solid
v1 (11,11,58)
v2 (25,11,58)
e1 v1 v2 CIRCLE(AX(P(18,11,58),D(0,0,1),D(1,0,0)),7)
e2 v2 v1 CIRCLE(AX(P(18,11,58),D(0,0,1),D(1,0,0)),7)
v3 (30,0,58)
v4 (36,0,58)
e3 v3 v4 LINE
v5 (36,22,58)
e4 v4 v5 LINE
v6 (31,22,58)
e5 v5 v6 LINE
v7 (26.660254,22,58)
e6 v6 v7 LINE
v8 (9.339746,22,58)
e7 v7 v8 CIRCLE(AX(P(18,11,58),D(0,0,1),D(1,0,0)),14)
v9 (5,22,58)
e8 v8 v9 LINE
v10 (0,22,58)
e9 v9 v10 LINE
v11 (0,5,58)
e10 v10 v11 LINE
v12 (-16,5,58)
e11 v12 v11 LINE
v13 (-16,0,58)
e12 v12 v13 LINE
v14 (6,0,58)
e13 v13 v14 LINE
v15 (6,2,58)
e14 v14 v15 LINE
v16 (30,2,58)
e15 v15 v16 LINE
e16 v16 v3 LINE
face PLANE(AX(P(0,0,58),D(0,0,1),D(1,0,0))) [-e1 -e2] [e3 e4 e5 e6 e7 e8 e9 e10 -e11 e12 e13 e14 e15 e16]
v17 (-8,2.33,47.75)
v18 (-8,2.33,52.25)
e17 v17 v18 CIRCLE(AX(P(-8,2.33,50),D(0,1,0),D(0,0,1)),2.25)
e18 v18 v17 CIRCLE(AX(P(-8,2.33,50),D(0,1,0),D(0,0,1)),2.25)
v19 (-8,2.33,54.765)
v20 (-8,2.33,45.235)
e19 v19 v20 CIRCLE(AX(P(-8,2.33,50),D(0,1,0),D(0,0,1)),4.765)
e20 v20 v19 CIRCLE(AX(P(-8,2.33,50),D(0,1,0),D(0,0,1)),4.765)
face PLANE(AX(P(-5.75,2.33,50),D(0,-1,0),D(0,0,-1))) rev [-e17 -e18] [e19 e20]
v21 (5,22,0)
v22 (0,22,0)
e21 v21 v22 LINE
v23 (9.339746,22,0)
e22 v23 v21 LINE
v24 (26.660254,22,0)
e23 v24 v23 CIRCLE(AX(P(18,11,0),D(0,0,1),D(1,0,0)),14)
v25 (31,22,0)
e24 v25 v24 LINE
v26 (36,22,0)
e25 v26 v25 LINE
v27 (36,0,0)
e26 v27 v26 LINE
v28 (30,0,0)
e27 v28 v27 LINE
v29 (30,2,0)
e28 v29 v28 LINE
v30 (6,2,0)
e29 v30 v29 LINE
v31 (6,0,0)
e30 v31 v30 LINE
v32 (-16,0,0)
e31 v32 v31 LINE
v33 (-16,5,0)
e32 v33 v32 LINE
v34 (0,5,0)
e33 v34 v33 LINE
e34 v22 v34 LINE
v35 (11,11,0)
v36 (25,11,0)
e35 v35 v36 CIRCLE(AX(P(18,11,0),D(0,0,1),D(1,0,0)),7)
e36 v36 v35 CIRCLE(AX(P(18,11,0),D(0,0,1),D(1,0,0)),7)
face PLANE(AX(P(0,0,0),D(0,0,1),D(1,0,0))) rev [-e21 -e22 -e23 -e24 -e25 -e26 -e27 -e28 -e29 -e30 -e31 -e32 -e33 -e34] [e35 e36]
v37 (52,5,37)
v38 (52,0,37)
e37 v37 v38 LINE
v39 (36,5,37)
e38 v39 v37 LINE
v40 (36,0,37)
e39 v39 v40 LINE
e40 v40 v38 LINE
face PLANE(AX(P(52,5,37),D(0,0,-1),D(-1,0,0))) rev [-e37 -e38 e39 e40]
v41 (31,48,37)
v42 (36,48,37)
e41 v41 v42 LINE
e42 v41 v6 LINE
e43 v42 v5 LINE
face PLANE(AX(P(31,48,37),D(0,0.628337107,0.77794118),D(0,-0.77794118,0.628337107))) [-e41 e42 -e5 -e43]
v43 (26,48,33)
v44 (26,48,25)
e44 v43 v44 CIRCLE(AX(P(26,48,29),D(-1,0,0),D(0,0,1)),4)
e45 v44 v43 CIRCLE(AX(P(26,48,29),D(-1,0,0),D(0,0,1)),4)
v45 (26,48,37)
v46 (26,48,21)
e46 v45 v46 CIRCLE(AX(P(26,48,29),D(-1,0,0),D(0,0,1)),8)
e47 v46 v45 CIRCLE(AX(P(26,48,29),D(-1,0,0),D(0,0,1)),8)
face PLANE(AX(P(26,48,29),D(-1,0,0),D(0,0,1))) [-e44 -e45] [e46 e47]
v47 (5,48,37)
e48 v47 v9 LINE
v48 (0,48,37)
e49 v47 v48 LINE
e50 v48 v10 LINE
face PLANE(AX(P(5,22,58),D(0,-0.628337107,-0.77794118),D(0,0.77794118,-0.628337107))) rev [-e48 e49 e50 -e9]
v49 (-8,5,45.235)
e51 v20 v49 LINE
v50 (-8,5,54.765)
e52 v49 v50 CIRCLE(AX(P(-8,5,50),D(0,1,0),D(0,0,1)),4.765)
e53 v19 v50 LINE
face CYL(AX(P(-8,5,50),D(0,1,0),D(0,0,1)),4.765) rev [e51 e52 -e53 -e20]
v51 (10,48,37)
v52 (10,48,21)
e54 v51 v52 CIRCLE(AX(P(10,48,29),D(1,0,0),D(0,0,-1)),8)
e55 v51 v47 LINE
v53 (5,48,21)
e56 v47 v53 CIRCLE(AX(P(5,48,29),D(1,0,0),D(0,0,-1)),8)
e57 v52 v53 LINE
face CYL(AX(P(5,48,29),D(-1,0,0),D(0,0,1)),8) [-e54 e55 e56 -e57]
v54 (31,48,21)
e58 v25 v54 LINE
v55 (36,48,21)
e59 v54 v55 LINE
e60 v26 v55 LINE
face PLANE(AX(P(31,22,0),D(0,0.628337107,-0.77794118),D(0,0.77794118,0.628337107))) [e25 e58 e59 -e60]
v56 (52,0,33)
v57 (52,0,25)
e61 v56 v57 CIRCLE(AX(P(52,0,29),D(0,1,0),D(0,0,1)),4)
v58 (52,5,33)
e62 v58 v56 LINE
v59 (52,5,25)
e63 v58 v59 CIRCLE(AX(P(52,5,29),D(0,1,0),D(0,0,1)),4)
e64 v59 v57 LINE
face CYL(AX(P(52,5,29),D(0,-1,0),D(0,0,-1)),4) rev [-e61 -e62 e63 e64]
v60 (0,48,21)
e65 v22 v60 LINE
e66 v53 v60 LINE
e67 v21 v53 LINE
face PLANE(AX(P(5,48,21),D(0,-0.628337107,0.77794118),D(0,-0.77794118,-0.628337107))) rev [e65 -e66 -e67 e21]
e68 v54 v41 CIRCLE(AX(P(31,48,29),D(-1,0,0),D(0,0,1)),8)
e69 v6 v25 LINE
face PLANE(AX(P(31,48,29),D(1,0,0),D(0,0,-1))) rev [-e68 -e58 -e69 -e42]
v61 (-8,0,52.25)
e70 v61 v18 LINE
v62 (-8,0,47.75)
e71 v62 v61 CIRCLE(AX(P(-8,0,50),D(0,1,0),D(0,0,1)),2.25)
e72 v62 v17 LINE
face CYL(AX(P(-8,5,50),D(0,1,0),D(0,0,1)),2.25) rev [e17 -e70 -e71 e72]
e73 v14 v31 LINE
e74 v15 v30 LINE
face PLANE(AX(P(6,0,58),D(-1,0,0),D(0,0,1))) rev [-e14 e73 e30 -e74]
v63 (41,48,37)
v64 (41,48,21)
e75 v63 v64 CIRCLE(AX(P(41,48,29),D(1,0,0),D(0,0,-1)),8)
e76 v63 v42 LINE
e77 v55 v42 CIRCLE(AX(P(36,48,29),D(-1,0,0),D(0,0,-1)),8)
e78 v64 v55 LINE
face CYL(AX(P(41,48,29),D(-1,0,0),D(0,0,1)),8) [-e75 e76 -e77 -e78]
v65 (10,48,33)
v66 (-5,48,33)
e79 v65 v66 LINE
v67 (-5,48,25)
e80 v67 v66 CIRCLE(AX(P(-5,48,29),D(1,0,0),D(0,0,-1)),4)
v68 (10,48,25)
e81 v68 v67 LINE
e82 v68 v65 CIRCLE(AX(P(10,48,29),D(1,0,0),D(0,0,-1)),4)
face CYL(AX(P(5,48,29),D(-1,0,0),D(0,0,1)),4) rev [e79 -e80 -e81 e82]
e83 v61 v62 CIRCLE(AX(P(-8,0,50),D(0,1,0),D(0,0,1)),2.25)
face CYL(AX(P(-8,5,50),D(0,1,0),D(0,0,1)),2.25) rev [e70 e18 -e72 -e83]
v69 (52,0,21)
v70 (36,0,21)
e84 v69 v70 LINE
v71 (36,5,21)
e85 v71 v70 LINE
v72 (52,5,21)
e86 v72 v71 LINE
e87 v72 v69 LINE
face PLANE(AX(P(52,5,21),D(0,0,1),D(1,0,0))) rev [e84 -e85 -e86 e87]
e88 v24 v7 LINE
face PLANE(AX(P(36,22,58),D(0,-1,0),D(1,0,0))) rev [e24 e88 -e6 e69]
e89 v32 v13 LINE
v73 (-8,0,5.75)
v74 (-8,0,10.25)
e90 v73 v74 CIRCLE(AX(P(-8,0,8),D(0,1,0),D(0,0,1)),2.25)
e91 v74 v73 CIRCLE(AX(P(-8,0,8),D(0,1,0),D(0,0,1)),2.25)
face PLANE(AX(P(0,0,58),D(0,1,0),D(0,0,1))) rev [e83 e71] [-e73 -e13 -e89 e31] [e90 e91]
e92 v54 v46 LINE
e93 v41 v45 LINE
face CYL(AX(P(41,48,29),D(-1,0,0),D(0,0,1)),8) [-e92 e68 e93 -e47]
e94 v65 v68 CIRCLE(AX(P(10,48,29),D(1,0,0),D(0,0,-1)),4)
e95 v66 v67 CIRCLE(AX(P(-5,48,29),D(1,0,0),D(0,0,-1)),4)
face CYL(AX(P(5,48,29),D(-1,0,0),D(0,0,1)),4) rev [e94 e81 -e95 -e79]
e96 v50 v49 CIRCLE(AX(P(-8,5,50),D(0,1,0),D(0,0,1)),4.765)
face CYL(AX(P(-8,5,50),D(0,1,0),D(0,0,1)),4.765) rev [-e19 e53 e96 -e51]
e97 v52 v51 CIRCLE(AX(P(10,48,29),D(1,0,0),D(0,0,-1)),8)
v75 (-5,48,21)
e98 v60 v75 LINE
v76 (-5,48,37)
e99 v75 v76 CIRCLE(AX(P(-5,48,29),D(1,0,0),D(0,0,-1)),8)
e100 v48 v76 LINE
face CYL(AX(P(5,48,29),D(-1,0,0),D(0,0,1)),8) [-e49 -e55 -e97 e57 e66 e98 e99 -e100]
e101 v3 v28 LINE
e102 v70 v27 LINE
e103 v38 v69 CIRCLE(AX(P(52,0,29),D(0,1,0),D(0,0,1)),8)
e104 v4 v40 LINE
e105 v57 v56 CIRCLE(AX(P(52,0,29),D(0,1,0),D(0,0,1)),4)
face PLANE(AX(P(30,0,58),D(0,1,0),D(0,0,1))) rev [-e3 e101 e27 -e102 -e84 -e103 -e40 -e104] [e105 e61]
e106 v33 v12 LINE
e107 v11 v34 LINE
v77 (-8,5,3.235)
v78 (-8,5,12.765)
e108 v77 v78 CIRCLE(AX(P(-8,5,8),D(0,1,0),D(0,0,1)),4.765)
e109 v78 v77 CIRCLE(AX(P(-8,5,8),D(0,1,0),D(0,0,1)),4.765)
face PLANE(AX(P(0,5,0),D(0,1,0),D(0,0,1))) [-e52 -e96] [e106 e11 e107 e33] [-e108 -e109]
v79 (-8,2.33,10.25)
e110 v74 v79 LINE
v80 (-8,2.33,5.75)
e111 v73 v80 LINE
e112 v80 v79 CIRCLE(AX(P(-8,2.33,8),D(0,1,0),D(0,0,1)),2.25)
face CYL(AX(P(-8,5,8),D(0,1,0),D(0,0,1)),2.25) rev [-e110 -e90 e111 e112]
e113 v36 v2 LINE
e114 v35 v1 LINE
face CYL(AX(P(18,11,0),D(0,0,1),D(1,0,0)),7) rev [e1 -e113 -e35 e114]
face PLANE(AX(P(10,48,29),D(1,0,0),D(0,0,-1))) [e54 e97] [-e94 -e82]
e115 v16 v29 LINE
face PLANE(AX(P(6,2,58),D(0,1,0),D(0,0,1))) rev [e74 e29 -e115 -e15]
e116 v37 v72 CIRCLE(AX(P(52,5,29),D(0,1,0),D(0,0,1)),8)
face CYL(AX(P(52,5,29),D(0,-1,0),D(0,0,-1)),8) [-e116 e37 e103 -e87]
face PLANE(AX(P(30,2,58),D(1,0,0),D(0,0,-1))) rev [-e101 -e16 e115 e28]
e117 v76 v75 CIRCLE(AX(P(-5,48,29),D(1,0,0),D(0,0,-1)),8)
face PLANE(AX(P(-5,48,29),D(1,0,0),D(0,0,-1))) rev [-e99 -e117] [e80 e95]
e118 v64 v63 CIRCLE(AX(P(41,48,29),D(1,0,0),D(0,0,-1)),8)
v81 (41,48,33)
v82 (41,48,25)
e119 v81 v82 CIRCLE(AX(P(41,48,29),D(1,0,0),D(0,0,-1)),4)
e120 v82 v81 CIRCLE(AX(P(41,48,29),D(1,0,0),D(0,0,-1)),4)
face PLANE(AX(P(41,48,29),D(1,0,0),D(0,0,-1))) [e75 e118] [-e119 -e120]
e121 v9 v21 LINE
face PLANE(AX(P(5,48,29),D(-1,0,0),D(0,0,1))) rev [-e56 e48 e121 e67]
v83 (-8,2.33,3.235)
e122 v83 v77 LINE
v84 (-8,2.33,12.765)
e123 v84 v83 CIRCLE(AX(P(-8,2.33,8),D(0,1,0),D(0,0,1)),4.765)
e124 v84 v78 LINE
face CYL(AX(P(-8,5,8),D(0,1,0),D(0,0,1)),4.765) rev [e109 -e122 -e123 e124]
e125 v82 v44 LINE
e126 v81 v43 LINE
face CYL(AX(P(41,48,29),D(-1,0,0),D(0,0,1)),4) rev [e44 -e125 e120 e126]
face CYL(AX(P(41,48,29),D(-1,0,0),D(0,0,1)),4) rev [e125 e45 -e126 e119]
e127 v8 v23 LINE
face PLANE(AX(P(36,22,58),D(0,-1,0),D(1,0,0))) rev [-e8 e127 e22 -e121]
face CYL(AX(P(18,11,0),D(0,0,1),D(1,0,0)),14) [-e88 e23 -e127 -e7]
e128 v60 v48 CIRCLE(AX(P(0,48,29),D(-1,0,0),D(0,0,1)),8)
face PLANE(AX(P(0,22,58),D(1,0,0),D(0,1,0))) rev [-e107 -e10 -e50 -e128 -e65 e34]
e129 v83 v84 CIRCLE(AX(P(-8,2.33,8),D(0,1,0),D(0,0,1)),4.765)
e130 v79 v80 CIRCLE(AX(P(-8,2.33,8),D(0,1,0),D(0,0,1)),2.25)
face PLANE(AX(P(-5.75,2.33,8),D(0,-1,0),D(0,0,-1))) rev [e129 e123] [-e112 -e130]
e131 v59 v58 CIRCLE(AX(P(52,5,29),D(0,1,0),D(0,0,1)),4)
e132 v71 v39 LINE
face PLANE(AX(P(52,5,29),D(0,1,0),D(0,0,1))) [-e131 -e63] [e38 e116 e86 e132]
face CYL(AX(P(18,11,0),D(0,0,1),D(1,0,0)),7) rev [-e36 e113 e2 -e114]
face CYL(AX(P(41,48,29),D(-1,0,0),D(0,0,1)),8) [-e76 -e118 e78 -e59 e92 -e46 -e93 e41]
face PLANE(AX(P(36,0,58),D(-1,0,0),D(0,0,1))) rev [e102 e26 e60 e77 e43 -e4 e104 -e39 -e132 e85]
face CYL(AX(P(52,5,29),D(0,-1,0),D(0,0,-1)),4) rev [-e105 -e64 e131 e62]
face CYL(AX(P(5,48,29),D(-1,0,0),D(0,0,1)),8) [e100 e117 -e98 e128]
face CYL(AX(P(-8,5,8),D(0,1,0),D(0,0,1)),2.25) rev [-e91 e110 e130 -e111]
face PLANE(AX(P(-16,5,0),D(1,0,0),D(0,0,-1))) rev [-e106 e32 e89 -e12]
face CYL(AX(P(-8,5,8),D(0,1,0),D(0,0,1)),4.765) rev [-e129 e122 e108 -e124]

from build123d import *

# Parameters (mm, degrees)
BASE_BLOCK_DEPTH                = 58
FRONT_BORE_BOSS_DEPTH           = 58
FRONT_BORE_SKETCH_R             = 7
FRONT_BORE_DEPTH                = 73.698005475
LEFT_ARM_SKETCH_R               = 8
LEFT_ARM_SKETCH_R_2             = 4
LEFT_ARM_DEPTH                  = 5
LEFT_ARM_WEB_DEPTH              = 5
LEFT_START                      = 5
LEFT_PIVOT_BOSS_SKETCH_R        = 8
LEFT_PIVOT_BOSS_DEPTH           = 5
LEFT_PIVOT_HOLE_SKETCH_R        = 4
LEFT_PIVOT_HOLE_DEPTH           = 85.711274338
RIGHT_ARM_SKETCH_R              = 8
RIGHT_ARM_SKETCH_R_2            = 4
RIGHT_ARM_DEPTH                 = 5
RIGHT_ARM_WEB_DEPTH             = 5
RIGHT_PIVOT_BOSS_SKETCH_R       = 8
RIGHT_PIVOT_BOSS_DEPTH          = 5
RIGHT_PIVOT_HOLE_8_SKETCH_R     = 4
RIGHT_PIVOT_HOLE_8_DEPTH        = 87.377080293
SIDE_LUG_SKETCH_R               = 4
SIDE_LUG_DEPTH                  = 5
MOUNTING_TAB_SKETCH_W           = 16
MOUNTING_TAB_SKETCH_H           = 58
MOUNTING_TAB_DEPTH              = 5
M5_COUNTERBORE_HOLE_D           = 4.5
M5_COUNTERBORE_HOLE_CBORE_D     = 9.53
M5_COUNTERBORE_HOLE_CBORE_DEPTH = 2.67


with BuildPart() as part:
    # Base Block Profile → Base Block (new body)
    with BuildSketch(Plane.XY):
        Polygon((0, 0), (6, 0), (6, 2), (30, 2), (30, 0), (36, 0), (36, 22), (0, 22), align=None)
    extrude(amount=BASE_BLOCK_DEPTH)

    # Front Bore Boss Sketch → Front Bore Boss (add, through all)
    with BuildSketch(Plane.XY.offset(58)):
        with BuildLine():
            Line((4, 11), (32, 11))
            ThreePointArc((32, 11), (18, 25), (4, 11))
        make_face()
    extrude(amount=-FRONT_BORE_BOSS_DEPTH)

    # Front Bore Sketch → Front Bore (cut, through all)
    with BuildSketch(Plane.XY.offset(58)):
        with Locations((18, 11)):
            Circle(FRONT_BORE_SKETCH_R)
    extrude(amount=-FRONT_BORE_DEPTH, mode=Mode.SUBTRACT)



with BuildPart() as body_2:
    # Left Arm Sketch → Left Arm (new, symmetric)
    with BuildSketch(Plane(origin=(0, 0, 0), x_dir=(0, 0, -1), z_dir=(1, 0, 0))):
        with Locations((-29, 48)):
            Circle(LEFT_ARM_SKETCH_R)
        with Locations((-29, 48)):
            Circle(LEFT_ARM_SKETCH_R_2, mode=Mode.SUBTRACT)
    extrude(amount=LEFT_ARM_DEPTH, both=True)


with BuildPart() as part_1:
    add(part.part)

    add(body_2.part)  # Left Arm Web merges body 2
    # Left Arm Web Sketch → Left Arm Web (add)
    with BuildSketch(Plane(origin=(0, 0, 0), x_dir=(0, 0, -1), z_dir=(1, 0, 0))):
        with BuildLine():
            Line((-21, 48), (0, 22))
            Line((0, 22), (-58, 22))
            Line((-58, 22), (-37, 48))
            ThreePointArc((-37, 48), (-29, 40), (-21, 48))
        make_face()
    extrude(amount=LEFT_ARM_WEB_DEPTH)

    # Left Pivot Boss Sketch → Left Pivot Boss (add)
    with BuildSketch(Plane(origin=(5, 0, 0), x_dir=(0, 0, -1), z_dir=(1, 0, 0)).offset(LEFT_START)):
        with Locations((-29, 48)):
            Circle(LEFT_PIVOT_BOSS_SKETCH_R)
    extrude(amount=-LEFT_PIVOT_BOSS_DEPTH)

    # Left Pivot Hole Sketch → Left Pivot Hole (cut, through all)
    with BuildSketch(Plane(origin=(10, 0, 0), x_dir=(0, 0, -1), z_dir=(1, 0, 0))):
        with Locations((-29, 48)):
            Circle(LEFT_PIVOT_HOLE_SKETCH_R)
    extrude(amount=-LEFT_PIVOT_HOLE_DEPTH, mode=Mode.SUBTRACT)



with BuildPart() as body_2_2:
    # Right Arm Sketch → Right Arm (new, symmetric)
    with BuildSketch(Plane(origin=(36, 0, 0), x_dir=(0, 0, -1), z_dir=(1, 0, 0))):
        with Locations((-29, 48)):
            Circle(RIGHT_ARM_SKETCH_R)
        with Locations((-29, 48)):
            Circle(RIGHT_ARM_SKETCH_R_2, mode=Mode.SUBTRACT)
    extrude(amount=RIGHT_ARM_DEPTH, both=True)


with BuildPart() as part_2:
    add(part_1.part)

    add(body_2_2.part)  # Right Arm Web merges body 2 2
    # Right Arm Web Sketch → Right Arm Web (add)
    with BuildSketch(Plane(origin=(36, 0, 0), x_dir=(0, 0, -1), z_dir=(1, 0, 0))):
        with BuildLine():
            Line((-37, 48), (-58, 22))
            Line((-58, 22), (0, 22))
            Line((0, 22), (-21, 48))
            ThreePointArc((-21, 48), (-29, 40), (-37, 48))
        make_face()
    extrude(amount=-RIGHT_ARM_WEB_DEPTH)

    # Right Pivot Boss Sketch → Right Pivot Boss (add)
    with BuildSketch(Plane.ZY.offset(-31)):
        with Locations(Location((29, 48, 0), (0, 0, 180))):
            Circle(RIGHT_PIVOT_BOSS_SKETCH_R)
    extrude(amount=RIGHT_PIVOT_BOSS_DEPTH)

    # Right Pivot Hole Ø8 Sketch → Right Pivot Hole Ø8 (cut, through all)
    with BuildSketch(Plane.ZY.offset(-26)):
        with Locations(Location((29, 48, 0), (0, 0, 180))):
            Circle(RIGHT_PIVOT_HOLE_8_SKETCH_R)
    extrude(amount=-RIGHT_PIVOT_HOLE_8_DEPTH, mode=Mode.SUBTRACT)

    # Side Lug Sketch → Side Lug (add)
    with BuildSketch(Plane(origin=(0, 0, 0), x_dir=(1, 0, 0), z_dir=(0, 1, 0))):
        with BuildLine():
            Line((52, -21), (36, -21))
            Line((36, -21), (36, -37))
            Line((36, -37), (52, -37))
            ThreePointArc((52, -37), (60, -29), (52, -21))
        make_face()
        with Locations(Location((52, -29, 0), (0, 0, 270))):
            Circle(SIDE_LUG_SKETCH_R, mode=Mode.SUBTRACT)
    extrude(amount=SIDE_LUG_DEPTH)

    # Mounting Tab Sketch → Mounting Tab (add)
    with BuildSketch(Plane(origin=(0, 0, 0), x_dir=(1, 0, 0), z_dir=(0, 1, 0))):
        with Locations((-8, -29)):
            Rectangle(MOUNTING_TAB_SKETCH_W, MOUNTING_TAB_SKETCH_H)
    extrude(amount=MOUNTING_TAB_DEPTH)

    # M5 Counterbore Hole (through all)
    with Locations(Plane(origin=(0, 5, 0), x_dir=(1, 0, 0), z_dir=(0, 1, 0))):
        with Locations((-8, -8), (-8, -50)):
            CounterBoreHole(M5_COUNTERBORE_HOLE_D / 2, M5_COUNTERBORE_HOLE_CBORE_D / 2, M5_COUNTERBORE_HOLE_CBORE_DEPTH)


solid = part_2.part
